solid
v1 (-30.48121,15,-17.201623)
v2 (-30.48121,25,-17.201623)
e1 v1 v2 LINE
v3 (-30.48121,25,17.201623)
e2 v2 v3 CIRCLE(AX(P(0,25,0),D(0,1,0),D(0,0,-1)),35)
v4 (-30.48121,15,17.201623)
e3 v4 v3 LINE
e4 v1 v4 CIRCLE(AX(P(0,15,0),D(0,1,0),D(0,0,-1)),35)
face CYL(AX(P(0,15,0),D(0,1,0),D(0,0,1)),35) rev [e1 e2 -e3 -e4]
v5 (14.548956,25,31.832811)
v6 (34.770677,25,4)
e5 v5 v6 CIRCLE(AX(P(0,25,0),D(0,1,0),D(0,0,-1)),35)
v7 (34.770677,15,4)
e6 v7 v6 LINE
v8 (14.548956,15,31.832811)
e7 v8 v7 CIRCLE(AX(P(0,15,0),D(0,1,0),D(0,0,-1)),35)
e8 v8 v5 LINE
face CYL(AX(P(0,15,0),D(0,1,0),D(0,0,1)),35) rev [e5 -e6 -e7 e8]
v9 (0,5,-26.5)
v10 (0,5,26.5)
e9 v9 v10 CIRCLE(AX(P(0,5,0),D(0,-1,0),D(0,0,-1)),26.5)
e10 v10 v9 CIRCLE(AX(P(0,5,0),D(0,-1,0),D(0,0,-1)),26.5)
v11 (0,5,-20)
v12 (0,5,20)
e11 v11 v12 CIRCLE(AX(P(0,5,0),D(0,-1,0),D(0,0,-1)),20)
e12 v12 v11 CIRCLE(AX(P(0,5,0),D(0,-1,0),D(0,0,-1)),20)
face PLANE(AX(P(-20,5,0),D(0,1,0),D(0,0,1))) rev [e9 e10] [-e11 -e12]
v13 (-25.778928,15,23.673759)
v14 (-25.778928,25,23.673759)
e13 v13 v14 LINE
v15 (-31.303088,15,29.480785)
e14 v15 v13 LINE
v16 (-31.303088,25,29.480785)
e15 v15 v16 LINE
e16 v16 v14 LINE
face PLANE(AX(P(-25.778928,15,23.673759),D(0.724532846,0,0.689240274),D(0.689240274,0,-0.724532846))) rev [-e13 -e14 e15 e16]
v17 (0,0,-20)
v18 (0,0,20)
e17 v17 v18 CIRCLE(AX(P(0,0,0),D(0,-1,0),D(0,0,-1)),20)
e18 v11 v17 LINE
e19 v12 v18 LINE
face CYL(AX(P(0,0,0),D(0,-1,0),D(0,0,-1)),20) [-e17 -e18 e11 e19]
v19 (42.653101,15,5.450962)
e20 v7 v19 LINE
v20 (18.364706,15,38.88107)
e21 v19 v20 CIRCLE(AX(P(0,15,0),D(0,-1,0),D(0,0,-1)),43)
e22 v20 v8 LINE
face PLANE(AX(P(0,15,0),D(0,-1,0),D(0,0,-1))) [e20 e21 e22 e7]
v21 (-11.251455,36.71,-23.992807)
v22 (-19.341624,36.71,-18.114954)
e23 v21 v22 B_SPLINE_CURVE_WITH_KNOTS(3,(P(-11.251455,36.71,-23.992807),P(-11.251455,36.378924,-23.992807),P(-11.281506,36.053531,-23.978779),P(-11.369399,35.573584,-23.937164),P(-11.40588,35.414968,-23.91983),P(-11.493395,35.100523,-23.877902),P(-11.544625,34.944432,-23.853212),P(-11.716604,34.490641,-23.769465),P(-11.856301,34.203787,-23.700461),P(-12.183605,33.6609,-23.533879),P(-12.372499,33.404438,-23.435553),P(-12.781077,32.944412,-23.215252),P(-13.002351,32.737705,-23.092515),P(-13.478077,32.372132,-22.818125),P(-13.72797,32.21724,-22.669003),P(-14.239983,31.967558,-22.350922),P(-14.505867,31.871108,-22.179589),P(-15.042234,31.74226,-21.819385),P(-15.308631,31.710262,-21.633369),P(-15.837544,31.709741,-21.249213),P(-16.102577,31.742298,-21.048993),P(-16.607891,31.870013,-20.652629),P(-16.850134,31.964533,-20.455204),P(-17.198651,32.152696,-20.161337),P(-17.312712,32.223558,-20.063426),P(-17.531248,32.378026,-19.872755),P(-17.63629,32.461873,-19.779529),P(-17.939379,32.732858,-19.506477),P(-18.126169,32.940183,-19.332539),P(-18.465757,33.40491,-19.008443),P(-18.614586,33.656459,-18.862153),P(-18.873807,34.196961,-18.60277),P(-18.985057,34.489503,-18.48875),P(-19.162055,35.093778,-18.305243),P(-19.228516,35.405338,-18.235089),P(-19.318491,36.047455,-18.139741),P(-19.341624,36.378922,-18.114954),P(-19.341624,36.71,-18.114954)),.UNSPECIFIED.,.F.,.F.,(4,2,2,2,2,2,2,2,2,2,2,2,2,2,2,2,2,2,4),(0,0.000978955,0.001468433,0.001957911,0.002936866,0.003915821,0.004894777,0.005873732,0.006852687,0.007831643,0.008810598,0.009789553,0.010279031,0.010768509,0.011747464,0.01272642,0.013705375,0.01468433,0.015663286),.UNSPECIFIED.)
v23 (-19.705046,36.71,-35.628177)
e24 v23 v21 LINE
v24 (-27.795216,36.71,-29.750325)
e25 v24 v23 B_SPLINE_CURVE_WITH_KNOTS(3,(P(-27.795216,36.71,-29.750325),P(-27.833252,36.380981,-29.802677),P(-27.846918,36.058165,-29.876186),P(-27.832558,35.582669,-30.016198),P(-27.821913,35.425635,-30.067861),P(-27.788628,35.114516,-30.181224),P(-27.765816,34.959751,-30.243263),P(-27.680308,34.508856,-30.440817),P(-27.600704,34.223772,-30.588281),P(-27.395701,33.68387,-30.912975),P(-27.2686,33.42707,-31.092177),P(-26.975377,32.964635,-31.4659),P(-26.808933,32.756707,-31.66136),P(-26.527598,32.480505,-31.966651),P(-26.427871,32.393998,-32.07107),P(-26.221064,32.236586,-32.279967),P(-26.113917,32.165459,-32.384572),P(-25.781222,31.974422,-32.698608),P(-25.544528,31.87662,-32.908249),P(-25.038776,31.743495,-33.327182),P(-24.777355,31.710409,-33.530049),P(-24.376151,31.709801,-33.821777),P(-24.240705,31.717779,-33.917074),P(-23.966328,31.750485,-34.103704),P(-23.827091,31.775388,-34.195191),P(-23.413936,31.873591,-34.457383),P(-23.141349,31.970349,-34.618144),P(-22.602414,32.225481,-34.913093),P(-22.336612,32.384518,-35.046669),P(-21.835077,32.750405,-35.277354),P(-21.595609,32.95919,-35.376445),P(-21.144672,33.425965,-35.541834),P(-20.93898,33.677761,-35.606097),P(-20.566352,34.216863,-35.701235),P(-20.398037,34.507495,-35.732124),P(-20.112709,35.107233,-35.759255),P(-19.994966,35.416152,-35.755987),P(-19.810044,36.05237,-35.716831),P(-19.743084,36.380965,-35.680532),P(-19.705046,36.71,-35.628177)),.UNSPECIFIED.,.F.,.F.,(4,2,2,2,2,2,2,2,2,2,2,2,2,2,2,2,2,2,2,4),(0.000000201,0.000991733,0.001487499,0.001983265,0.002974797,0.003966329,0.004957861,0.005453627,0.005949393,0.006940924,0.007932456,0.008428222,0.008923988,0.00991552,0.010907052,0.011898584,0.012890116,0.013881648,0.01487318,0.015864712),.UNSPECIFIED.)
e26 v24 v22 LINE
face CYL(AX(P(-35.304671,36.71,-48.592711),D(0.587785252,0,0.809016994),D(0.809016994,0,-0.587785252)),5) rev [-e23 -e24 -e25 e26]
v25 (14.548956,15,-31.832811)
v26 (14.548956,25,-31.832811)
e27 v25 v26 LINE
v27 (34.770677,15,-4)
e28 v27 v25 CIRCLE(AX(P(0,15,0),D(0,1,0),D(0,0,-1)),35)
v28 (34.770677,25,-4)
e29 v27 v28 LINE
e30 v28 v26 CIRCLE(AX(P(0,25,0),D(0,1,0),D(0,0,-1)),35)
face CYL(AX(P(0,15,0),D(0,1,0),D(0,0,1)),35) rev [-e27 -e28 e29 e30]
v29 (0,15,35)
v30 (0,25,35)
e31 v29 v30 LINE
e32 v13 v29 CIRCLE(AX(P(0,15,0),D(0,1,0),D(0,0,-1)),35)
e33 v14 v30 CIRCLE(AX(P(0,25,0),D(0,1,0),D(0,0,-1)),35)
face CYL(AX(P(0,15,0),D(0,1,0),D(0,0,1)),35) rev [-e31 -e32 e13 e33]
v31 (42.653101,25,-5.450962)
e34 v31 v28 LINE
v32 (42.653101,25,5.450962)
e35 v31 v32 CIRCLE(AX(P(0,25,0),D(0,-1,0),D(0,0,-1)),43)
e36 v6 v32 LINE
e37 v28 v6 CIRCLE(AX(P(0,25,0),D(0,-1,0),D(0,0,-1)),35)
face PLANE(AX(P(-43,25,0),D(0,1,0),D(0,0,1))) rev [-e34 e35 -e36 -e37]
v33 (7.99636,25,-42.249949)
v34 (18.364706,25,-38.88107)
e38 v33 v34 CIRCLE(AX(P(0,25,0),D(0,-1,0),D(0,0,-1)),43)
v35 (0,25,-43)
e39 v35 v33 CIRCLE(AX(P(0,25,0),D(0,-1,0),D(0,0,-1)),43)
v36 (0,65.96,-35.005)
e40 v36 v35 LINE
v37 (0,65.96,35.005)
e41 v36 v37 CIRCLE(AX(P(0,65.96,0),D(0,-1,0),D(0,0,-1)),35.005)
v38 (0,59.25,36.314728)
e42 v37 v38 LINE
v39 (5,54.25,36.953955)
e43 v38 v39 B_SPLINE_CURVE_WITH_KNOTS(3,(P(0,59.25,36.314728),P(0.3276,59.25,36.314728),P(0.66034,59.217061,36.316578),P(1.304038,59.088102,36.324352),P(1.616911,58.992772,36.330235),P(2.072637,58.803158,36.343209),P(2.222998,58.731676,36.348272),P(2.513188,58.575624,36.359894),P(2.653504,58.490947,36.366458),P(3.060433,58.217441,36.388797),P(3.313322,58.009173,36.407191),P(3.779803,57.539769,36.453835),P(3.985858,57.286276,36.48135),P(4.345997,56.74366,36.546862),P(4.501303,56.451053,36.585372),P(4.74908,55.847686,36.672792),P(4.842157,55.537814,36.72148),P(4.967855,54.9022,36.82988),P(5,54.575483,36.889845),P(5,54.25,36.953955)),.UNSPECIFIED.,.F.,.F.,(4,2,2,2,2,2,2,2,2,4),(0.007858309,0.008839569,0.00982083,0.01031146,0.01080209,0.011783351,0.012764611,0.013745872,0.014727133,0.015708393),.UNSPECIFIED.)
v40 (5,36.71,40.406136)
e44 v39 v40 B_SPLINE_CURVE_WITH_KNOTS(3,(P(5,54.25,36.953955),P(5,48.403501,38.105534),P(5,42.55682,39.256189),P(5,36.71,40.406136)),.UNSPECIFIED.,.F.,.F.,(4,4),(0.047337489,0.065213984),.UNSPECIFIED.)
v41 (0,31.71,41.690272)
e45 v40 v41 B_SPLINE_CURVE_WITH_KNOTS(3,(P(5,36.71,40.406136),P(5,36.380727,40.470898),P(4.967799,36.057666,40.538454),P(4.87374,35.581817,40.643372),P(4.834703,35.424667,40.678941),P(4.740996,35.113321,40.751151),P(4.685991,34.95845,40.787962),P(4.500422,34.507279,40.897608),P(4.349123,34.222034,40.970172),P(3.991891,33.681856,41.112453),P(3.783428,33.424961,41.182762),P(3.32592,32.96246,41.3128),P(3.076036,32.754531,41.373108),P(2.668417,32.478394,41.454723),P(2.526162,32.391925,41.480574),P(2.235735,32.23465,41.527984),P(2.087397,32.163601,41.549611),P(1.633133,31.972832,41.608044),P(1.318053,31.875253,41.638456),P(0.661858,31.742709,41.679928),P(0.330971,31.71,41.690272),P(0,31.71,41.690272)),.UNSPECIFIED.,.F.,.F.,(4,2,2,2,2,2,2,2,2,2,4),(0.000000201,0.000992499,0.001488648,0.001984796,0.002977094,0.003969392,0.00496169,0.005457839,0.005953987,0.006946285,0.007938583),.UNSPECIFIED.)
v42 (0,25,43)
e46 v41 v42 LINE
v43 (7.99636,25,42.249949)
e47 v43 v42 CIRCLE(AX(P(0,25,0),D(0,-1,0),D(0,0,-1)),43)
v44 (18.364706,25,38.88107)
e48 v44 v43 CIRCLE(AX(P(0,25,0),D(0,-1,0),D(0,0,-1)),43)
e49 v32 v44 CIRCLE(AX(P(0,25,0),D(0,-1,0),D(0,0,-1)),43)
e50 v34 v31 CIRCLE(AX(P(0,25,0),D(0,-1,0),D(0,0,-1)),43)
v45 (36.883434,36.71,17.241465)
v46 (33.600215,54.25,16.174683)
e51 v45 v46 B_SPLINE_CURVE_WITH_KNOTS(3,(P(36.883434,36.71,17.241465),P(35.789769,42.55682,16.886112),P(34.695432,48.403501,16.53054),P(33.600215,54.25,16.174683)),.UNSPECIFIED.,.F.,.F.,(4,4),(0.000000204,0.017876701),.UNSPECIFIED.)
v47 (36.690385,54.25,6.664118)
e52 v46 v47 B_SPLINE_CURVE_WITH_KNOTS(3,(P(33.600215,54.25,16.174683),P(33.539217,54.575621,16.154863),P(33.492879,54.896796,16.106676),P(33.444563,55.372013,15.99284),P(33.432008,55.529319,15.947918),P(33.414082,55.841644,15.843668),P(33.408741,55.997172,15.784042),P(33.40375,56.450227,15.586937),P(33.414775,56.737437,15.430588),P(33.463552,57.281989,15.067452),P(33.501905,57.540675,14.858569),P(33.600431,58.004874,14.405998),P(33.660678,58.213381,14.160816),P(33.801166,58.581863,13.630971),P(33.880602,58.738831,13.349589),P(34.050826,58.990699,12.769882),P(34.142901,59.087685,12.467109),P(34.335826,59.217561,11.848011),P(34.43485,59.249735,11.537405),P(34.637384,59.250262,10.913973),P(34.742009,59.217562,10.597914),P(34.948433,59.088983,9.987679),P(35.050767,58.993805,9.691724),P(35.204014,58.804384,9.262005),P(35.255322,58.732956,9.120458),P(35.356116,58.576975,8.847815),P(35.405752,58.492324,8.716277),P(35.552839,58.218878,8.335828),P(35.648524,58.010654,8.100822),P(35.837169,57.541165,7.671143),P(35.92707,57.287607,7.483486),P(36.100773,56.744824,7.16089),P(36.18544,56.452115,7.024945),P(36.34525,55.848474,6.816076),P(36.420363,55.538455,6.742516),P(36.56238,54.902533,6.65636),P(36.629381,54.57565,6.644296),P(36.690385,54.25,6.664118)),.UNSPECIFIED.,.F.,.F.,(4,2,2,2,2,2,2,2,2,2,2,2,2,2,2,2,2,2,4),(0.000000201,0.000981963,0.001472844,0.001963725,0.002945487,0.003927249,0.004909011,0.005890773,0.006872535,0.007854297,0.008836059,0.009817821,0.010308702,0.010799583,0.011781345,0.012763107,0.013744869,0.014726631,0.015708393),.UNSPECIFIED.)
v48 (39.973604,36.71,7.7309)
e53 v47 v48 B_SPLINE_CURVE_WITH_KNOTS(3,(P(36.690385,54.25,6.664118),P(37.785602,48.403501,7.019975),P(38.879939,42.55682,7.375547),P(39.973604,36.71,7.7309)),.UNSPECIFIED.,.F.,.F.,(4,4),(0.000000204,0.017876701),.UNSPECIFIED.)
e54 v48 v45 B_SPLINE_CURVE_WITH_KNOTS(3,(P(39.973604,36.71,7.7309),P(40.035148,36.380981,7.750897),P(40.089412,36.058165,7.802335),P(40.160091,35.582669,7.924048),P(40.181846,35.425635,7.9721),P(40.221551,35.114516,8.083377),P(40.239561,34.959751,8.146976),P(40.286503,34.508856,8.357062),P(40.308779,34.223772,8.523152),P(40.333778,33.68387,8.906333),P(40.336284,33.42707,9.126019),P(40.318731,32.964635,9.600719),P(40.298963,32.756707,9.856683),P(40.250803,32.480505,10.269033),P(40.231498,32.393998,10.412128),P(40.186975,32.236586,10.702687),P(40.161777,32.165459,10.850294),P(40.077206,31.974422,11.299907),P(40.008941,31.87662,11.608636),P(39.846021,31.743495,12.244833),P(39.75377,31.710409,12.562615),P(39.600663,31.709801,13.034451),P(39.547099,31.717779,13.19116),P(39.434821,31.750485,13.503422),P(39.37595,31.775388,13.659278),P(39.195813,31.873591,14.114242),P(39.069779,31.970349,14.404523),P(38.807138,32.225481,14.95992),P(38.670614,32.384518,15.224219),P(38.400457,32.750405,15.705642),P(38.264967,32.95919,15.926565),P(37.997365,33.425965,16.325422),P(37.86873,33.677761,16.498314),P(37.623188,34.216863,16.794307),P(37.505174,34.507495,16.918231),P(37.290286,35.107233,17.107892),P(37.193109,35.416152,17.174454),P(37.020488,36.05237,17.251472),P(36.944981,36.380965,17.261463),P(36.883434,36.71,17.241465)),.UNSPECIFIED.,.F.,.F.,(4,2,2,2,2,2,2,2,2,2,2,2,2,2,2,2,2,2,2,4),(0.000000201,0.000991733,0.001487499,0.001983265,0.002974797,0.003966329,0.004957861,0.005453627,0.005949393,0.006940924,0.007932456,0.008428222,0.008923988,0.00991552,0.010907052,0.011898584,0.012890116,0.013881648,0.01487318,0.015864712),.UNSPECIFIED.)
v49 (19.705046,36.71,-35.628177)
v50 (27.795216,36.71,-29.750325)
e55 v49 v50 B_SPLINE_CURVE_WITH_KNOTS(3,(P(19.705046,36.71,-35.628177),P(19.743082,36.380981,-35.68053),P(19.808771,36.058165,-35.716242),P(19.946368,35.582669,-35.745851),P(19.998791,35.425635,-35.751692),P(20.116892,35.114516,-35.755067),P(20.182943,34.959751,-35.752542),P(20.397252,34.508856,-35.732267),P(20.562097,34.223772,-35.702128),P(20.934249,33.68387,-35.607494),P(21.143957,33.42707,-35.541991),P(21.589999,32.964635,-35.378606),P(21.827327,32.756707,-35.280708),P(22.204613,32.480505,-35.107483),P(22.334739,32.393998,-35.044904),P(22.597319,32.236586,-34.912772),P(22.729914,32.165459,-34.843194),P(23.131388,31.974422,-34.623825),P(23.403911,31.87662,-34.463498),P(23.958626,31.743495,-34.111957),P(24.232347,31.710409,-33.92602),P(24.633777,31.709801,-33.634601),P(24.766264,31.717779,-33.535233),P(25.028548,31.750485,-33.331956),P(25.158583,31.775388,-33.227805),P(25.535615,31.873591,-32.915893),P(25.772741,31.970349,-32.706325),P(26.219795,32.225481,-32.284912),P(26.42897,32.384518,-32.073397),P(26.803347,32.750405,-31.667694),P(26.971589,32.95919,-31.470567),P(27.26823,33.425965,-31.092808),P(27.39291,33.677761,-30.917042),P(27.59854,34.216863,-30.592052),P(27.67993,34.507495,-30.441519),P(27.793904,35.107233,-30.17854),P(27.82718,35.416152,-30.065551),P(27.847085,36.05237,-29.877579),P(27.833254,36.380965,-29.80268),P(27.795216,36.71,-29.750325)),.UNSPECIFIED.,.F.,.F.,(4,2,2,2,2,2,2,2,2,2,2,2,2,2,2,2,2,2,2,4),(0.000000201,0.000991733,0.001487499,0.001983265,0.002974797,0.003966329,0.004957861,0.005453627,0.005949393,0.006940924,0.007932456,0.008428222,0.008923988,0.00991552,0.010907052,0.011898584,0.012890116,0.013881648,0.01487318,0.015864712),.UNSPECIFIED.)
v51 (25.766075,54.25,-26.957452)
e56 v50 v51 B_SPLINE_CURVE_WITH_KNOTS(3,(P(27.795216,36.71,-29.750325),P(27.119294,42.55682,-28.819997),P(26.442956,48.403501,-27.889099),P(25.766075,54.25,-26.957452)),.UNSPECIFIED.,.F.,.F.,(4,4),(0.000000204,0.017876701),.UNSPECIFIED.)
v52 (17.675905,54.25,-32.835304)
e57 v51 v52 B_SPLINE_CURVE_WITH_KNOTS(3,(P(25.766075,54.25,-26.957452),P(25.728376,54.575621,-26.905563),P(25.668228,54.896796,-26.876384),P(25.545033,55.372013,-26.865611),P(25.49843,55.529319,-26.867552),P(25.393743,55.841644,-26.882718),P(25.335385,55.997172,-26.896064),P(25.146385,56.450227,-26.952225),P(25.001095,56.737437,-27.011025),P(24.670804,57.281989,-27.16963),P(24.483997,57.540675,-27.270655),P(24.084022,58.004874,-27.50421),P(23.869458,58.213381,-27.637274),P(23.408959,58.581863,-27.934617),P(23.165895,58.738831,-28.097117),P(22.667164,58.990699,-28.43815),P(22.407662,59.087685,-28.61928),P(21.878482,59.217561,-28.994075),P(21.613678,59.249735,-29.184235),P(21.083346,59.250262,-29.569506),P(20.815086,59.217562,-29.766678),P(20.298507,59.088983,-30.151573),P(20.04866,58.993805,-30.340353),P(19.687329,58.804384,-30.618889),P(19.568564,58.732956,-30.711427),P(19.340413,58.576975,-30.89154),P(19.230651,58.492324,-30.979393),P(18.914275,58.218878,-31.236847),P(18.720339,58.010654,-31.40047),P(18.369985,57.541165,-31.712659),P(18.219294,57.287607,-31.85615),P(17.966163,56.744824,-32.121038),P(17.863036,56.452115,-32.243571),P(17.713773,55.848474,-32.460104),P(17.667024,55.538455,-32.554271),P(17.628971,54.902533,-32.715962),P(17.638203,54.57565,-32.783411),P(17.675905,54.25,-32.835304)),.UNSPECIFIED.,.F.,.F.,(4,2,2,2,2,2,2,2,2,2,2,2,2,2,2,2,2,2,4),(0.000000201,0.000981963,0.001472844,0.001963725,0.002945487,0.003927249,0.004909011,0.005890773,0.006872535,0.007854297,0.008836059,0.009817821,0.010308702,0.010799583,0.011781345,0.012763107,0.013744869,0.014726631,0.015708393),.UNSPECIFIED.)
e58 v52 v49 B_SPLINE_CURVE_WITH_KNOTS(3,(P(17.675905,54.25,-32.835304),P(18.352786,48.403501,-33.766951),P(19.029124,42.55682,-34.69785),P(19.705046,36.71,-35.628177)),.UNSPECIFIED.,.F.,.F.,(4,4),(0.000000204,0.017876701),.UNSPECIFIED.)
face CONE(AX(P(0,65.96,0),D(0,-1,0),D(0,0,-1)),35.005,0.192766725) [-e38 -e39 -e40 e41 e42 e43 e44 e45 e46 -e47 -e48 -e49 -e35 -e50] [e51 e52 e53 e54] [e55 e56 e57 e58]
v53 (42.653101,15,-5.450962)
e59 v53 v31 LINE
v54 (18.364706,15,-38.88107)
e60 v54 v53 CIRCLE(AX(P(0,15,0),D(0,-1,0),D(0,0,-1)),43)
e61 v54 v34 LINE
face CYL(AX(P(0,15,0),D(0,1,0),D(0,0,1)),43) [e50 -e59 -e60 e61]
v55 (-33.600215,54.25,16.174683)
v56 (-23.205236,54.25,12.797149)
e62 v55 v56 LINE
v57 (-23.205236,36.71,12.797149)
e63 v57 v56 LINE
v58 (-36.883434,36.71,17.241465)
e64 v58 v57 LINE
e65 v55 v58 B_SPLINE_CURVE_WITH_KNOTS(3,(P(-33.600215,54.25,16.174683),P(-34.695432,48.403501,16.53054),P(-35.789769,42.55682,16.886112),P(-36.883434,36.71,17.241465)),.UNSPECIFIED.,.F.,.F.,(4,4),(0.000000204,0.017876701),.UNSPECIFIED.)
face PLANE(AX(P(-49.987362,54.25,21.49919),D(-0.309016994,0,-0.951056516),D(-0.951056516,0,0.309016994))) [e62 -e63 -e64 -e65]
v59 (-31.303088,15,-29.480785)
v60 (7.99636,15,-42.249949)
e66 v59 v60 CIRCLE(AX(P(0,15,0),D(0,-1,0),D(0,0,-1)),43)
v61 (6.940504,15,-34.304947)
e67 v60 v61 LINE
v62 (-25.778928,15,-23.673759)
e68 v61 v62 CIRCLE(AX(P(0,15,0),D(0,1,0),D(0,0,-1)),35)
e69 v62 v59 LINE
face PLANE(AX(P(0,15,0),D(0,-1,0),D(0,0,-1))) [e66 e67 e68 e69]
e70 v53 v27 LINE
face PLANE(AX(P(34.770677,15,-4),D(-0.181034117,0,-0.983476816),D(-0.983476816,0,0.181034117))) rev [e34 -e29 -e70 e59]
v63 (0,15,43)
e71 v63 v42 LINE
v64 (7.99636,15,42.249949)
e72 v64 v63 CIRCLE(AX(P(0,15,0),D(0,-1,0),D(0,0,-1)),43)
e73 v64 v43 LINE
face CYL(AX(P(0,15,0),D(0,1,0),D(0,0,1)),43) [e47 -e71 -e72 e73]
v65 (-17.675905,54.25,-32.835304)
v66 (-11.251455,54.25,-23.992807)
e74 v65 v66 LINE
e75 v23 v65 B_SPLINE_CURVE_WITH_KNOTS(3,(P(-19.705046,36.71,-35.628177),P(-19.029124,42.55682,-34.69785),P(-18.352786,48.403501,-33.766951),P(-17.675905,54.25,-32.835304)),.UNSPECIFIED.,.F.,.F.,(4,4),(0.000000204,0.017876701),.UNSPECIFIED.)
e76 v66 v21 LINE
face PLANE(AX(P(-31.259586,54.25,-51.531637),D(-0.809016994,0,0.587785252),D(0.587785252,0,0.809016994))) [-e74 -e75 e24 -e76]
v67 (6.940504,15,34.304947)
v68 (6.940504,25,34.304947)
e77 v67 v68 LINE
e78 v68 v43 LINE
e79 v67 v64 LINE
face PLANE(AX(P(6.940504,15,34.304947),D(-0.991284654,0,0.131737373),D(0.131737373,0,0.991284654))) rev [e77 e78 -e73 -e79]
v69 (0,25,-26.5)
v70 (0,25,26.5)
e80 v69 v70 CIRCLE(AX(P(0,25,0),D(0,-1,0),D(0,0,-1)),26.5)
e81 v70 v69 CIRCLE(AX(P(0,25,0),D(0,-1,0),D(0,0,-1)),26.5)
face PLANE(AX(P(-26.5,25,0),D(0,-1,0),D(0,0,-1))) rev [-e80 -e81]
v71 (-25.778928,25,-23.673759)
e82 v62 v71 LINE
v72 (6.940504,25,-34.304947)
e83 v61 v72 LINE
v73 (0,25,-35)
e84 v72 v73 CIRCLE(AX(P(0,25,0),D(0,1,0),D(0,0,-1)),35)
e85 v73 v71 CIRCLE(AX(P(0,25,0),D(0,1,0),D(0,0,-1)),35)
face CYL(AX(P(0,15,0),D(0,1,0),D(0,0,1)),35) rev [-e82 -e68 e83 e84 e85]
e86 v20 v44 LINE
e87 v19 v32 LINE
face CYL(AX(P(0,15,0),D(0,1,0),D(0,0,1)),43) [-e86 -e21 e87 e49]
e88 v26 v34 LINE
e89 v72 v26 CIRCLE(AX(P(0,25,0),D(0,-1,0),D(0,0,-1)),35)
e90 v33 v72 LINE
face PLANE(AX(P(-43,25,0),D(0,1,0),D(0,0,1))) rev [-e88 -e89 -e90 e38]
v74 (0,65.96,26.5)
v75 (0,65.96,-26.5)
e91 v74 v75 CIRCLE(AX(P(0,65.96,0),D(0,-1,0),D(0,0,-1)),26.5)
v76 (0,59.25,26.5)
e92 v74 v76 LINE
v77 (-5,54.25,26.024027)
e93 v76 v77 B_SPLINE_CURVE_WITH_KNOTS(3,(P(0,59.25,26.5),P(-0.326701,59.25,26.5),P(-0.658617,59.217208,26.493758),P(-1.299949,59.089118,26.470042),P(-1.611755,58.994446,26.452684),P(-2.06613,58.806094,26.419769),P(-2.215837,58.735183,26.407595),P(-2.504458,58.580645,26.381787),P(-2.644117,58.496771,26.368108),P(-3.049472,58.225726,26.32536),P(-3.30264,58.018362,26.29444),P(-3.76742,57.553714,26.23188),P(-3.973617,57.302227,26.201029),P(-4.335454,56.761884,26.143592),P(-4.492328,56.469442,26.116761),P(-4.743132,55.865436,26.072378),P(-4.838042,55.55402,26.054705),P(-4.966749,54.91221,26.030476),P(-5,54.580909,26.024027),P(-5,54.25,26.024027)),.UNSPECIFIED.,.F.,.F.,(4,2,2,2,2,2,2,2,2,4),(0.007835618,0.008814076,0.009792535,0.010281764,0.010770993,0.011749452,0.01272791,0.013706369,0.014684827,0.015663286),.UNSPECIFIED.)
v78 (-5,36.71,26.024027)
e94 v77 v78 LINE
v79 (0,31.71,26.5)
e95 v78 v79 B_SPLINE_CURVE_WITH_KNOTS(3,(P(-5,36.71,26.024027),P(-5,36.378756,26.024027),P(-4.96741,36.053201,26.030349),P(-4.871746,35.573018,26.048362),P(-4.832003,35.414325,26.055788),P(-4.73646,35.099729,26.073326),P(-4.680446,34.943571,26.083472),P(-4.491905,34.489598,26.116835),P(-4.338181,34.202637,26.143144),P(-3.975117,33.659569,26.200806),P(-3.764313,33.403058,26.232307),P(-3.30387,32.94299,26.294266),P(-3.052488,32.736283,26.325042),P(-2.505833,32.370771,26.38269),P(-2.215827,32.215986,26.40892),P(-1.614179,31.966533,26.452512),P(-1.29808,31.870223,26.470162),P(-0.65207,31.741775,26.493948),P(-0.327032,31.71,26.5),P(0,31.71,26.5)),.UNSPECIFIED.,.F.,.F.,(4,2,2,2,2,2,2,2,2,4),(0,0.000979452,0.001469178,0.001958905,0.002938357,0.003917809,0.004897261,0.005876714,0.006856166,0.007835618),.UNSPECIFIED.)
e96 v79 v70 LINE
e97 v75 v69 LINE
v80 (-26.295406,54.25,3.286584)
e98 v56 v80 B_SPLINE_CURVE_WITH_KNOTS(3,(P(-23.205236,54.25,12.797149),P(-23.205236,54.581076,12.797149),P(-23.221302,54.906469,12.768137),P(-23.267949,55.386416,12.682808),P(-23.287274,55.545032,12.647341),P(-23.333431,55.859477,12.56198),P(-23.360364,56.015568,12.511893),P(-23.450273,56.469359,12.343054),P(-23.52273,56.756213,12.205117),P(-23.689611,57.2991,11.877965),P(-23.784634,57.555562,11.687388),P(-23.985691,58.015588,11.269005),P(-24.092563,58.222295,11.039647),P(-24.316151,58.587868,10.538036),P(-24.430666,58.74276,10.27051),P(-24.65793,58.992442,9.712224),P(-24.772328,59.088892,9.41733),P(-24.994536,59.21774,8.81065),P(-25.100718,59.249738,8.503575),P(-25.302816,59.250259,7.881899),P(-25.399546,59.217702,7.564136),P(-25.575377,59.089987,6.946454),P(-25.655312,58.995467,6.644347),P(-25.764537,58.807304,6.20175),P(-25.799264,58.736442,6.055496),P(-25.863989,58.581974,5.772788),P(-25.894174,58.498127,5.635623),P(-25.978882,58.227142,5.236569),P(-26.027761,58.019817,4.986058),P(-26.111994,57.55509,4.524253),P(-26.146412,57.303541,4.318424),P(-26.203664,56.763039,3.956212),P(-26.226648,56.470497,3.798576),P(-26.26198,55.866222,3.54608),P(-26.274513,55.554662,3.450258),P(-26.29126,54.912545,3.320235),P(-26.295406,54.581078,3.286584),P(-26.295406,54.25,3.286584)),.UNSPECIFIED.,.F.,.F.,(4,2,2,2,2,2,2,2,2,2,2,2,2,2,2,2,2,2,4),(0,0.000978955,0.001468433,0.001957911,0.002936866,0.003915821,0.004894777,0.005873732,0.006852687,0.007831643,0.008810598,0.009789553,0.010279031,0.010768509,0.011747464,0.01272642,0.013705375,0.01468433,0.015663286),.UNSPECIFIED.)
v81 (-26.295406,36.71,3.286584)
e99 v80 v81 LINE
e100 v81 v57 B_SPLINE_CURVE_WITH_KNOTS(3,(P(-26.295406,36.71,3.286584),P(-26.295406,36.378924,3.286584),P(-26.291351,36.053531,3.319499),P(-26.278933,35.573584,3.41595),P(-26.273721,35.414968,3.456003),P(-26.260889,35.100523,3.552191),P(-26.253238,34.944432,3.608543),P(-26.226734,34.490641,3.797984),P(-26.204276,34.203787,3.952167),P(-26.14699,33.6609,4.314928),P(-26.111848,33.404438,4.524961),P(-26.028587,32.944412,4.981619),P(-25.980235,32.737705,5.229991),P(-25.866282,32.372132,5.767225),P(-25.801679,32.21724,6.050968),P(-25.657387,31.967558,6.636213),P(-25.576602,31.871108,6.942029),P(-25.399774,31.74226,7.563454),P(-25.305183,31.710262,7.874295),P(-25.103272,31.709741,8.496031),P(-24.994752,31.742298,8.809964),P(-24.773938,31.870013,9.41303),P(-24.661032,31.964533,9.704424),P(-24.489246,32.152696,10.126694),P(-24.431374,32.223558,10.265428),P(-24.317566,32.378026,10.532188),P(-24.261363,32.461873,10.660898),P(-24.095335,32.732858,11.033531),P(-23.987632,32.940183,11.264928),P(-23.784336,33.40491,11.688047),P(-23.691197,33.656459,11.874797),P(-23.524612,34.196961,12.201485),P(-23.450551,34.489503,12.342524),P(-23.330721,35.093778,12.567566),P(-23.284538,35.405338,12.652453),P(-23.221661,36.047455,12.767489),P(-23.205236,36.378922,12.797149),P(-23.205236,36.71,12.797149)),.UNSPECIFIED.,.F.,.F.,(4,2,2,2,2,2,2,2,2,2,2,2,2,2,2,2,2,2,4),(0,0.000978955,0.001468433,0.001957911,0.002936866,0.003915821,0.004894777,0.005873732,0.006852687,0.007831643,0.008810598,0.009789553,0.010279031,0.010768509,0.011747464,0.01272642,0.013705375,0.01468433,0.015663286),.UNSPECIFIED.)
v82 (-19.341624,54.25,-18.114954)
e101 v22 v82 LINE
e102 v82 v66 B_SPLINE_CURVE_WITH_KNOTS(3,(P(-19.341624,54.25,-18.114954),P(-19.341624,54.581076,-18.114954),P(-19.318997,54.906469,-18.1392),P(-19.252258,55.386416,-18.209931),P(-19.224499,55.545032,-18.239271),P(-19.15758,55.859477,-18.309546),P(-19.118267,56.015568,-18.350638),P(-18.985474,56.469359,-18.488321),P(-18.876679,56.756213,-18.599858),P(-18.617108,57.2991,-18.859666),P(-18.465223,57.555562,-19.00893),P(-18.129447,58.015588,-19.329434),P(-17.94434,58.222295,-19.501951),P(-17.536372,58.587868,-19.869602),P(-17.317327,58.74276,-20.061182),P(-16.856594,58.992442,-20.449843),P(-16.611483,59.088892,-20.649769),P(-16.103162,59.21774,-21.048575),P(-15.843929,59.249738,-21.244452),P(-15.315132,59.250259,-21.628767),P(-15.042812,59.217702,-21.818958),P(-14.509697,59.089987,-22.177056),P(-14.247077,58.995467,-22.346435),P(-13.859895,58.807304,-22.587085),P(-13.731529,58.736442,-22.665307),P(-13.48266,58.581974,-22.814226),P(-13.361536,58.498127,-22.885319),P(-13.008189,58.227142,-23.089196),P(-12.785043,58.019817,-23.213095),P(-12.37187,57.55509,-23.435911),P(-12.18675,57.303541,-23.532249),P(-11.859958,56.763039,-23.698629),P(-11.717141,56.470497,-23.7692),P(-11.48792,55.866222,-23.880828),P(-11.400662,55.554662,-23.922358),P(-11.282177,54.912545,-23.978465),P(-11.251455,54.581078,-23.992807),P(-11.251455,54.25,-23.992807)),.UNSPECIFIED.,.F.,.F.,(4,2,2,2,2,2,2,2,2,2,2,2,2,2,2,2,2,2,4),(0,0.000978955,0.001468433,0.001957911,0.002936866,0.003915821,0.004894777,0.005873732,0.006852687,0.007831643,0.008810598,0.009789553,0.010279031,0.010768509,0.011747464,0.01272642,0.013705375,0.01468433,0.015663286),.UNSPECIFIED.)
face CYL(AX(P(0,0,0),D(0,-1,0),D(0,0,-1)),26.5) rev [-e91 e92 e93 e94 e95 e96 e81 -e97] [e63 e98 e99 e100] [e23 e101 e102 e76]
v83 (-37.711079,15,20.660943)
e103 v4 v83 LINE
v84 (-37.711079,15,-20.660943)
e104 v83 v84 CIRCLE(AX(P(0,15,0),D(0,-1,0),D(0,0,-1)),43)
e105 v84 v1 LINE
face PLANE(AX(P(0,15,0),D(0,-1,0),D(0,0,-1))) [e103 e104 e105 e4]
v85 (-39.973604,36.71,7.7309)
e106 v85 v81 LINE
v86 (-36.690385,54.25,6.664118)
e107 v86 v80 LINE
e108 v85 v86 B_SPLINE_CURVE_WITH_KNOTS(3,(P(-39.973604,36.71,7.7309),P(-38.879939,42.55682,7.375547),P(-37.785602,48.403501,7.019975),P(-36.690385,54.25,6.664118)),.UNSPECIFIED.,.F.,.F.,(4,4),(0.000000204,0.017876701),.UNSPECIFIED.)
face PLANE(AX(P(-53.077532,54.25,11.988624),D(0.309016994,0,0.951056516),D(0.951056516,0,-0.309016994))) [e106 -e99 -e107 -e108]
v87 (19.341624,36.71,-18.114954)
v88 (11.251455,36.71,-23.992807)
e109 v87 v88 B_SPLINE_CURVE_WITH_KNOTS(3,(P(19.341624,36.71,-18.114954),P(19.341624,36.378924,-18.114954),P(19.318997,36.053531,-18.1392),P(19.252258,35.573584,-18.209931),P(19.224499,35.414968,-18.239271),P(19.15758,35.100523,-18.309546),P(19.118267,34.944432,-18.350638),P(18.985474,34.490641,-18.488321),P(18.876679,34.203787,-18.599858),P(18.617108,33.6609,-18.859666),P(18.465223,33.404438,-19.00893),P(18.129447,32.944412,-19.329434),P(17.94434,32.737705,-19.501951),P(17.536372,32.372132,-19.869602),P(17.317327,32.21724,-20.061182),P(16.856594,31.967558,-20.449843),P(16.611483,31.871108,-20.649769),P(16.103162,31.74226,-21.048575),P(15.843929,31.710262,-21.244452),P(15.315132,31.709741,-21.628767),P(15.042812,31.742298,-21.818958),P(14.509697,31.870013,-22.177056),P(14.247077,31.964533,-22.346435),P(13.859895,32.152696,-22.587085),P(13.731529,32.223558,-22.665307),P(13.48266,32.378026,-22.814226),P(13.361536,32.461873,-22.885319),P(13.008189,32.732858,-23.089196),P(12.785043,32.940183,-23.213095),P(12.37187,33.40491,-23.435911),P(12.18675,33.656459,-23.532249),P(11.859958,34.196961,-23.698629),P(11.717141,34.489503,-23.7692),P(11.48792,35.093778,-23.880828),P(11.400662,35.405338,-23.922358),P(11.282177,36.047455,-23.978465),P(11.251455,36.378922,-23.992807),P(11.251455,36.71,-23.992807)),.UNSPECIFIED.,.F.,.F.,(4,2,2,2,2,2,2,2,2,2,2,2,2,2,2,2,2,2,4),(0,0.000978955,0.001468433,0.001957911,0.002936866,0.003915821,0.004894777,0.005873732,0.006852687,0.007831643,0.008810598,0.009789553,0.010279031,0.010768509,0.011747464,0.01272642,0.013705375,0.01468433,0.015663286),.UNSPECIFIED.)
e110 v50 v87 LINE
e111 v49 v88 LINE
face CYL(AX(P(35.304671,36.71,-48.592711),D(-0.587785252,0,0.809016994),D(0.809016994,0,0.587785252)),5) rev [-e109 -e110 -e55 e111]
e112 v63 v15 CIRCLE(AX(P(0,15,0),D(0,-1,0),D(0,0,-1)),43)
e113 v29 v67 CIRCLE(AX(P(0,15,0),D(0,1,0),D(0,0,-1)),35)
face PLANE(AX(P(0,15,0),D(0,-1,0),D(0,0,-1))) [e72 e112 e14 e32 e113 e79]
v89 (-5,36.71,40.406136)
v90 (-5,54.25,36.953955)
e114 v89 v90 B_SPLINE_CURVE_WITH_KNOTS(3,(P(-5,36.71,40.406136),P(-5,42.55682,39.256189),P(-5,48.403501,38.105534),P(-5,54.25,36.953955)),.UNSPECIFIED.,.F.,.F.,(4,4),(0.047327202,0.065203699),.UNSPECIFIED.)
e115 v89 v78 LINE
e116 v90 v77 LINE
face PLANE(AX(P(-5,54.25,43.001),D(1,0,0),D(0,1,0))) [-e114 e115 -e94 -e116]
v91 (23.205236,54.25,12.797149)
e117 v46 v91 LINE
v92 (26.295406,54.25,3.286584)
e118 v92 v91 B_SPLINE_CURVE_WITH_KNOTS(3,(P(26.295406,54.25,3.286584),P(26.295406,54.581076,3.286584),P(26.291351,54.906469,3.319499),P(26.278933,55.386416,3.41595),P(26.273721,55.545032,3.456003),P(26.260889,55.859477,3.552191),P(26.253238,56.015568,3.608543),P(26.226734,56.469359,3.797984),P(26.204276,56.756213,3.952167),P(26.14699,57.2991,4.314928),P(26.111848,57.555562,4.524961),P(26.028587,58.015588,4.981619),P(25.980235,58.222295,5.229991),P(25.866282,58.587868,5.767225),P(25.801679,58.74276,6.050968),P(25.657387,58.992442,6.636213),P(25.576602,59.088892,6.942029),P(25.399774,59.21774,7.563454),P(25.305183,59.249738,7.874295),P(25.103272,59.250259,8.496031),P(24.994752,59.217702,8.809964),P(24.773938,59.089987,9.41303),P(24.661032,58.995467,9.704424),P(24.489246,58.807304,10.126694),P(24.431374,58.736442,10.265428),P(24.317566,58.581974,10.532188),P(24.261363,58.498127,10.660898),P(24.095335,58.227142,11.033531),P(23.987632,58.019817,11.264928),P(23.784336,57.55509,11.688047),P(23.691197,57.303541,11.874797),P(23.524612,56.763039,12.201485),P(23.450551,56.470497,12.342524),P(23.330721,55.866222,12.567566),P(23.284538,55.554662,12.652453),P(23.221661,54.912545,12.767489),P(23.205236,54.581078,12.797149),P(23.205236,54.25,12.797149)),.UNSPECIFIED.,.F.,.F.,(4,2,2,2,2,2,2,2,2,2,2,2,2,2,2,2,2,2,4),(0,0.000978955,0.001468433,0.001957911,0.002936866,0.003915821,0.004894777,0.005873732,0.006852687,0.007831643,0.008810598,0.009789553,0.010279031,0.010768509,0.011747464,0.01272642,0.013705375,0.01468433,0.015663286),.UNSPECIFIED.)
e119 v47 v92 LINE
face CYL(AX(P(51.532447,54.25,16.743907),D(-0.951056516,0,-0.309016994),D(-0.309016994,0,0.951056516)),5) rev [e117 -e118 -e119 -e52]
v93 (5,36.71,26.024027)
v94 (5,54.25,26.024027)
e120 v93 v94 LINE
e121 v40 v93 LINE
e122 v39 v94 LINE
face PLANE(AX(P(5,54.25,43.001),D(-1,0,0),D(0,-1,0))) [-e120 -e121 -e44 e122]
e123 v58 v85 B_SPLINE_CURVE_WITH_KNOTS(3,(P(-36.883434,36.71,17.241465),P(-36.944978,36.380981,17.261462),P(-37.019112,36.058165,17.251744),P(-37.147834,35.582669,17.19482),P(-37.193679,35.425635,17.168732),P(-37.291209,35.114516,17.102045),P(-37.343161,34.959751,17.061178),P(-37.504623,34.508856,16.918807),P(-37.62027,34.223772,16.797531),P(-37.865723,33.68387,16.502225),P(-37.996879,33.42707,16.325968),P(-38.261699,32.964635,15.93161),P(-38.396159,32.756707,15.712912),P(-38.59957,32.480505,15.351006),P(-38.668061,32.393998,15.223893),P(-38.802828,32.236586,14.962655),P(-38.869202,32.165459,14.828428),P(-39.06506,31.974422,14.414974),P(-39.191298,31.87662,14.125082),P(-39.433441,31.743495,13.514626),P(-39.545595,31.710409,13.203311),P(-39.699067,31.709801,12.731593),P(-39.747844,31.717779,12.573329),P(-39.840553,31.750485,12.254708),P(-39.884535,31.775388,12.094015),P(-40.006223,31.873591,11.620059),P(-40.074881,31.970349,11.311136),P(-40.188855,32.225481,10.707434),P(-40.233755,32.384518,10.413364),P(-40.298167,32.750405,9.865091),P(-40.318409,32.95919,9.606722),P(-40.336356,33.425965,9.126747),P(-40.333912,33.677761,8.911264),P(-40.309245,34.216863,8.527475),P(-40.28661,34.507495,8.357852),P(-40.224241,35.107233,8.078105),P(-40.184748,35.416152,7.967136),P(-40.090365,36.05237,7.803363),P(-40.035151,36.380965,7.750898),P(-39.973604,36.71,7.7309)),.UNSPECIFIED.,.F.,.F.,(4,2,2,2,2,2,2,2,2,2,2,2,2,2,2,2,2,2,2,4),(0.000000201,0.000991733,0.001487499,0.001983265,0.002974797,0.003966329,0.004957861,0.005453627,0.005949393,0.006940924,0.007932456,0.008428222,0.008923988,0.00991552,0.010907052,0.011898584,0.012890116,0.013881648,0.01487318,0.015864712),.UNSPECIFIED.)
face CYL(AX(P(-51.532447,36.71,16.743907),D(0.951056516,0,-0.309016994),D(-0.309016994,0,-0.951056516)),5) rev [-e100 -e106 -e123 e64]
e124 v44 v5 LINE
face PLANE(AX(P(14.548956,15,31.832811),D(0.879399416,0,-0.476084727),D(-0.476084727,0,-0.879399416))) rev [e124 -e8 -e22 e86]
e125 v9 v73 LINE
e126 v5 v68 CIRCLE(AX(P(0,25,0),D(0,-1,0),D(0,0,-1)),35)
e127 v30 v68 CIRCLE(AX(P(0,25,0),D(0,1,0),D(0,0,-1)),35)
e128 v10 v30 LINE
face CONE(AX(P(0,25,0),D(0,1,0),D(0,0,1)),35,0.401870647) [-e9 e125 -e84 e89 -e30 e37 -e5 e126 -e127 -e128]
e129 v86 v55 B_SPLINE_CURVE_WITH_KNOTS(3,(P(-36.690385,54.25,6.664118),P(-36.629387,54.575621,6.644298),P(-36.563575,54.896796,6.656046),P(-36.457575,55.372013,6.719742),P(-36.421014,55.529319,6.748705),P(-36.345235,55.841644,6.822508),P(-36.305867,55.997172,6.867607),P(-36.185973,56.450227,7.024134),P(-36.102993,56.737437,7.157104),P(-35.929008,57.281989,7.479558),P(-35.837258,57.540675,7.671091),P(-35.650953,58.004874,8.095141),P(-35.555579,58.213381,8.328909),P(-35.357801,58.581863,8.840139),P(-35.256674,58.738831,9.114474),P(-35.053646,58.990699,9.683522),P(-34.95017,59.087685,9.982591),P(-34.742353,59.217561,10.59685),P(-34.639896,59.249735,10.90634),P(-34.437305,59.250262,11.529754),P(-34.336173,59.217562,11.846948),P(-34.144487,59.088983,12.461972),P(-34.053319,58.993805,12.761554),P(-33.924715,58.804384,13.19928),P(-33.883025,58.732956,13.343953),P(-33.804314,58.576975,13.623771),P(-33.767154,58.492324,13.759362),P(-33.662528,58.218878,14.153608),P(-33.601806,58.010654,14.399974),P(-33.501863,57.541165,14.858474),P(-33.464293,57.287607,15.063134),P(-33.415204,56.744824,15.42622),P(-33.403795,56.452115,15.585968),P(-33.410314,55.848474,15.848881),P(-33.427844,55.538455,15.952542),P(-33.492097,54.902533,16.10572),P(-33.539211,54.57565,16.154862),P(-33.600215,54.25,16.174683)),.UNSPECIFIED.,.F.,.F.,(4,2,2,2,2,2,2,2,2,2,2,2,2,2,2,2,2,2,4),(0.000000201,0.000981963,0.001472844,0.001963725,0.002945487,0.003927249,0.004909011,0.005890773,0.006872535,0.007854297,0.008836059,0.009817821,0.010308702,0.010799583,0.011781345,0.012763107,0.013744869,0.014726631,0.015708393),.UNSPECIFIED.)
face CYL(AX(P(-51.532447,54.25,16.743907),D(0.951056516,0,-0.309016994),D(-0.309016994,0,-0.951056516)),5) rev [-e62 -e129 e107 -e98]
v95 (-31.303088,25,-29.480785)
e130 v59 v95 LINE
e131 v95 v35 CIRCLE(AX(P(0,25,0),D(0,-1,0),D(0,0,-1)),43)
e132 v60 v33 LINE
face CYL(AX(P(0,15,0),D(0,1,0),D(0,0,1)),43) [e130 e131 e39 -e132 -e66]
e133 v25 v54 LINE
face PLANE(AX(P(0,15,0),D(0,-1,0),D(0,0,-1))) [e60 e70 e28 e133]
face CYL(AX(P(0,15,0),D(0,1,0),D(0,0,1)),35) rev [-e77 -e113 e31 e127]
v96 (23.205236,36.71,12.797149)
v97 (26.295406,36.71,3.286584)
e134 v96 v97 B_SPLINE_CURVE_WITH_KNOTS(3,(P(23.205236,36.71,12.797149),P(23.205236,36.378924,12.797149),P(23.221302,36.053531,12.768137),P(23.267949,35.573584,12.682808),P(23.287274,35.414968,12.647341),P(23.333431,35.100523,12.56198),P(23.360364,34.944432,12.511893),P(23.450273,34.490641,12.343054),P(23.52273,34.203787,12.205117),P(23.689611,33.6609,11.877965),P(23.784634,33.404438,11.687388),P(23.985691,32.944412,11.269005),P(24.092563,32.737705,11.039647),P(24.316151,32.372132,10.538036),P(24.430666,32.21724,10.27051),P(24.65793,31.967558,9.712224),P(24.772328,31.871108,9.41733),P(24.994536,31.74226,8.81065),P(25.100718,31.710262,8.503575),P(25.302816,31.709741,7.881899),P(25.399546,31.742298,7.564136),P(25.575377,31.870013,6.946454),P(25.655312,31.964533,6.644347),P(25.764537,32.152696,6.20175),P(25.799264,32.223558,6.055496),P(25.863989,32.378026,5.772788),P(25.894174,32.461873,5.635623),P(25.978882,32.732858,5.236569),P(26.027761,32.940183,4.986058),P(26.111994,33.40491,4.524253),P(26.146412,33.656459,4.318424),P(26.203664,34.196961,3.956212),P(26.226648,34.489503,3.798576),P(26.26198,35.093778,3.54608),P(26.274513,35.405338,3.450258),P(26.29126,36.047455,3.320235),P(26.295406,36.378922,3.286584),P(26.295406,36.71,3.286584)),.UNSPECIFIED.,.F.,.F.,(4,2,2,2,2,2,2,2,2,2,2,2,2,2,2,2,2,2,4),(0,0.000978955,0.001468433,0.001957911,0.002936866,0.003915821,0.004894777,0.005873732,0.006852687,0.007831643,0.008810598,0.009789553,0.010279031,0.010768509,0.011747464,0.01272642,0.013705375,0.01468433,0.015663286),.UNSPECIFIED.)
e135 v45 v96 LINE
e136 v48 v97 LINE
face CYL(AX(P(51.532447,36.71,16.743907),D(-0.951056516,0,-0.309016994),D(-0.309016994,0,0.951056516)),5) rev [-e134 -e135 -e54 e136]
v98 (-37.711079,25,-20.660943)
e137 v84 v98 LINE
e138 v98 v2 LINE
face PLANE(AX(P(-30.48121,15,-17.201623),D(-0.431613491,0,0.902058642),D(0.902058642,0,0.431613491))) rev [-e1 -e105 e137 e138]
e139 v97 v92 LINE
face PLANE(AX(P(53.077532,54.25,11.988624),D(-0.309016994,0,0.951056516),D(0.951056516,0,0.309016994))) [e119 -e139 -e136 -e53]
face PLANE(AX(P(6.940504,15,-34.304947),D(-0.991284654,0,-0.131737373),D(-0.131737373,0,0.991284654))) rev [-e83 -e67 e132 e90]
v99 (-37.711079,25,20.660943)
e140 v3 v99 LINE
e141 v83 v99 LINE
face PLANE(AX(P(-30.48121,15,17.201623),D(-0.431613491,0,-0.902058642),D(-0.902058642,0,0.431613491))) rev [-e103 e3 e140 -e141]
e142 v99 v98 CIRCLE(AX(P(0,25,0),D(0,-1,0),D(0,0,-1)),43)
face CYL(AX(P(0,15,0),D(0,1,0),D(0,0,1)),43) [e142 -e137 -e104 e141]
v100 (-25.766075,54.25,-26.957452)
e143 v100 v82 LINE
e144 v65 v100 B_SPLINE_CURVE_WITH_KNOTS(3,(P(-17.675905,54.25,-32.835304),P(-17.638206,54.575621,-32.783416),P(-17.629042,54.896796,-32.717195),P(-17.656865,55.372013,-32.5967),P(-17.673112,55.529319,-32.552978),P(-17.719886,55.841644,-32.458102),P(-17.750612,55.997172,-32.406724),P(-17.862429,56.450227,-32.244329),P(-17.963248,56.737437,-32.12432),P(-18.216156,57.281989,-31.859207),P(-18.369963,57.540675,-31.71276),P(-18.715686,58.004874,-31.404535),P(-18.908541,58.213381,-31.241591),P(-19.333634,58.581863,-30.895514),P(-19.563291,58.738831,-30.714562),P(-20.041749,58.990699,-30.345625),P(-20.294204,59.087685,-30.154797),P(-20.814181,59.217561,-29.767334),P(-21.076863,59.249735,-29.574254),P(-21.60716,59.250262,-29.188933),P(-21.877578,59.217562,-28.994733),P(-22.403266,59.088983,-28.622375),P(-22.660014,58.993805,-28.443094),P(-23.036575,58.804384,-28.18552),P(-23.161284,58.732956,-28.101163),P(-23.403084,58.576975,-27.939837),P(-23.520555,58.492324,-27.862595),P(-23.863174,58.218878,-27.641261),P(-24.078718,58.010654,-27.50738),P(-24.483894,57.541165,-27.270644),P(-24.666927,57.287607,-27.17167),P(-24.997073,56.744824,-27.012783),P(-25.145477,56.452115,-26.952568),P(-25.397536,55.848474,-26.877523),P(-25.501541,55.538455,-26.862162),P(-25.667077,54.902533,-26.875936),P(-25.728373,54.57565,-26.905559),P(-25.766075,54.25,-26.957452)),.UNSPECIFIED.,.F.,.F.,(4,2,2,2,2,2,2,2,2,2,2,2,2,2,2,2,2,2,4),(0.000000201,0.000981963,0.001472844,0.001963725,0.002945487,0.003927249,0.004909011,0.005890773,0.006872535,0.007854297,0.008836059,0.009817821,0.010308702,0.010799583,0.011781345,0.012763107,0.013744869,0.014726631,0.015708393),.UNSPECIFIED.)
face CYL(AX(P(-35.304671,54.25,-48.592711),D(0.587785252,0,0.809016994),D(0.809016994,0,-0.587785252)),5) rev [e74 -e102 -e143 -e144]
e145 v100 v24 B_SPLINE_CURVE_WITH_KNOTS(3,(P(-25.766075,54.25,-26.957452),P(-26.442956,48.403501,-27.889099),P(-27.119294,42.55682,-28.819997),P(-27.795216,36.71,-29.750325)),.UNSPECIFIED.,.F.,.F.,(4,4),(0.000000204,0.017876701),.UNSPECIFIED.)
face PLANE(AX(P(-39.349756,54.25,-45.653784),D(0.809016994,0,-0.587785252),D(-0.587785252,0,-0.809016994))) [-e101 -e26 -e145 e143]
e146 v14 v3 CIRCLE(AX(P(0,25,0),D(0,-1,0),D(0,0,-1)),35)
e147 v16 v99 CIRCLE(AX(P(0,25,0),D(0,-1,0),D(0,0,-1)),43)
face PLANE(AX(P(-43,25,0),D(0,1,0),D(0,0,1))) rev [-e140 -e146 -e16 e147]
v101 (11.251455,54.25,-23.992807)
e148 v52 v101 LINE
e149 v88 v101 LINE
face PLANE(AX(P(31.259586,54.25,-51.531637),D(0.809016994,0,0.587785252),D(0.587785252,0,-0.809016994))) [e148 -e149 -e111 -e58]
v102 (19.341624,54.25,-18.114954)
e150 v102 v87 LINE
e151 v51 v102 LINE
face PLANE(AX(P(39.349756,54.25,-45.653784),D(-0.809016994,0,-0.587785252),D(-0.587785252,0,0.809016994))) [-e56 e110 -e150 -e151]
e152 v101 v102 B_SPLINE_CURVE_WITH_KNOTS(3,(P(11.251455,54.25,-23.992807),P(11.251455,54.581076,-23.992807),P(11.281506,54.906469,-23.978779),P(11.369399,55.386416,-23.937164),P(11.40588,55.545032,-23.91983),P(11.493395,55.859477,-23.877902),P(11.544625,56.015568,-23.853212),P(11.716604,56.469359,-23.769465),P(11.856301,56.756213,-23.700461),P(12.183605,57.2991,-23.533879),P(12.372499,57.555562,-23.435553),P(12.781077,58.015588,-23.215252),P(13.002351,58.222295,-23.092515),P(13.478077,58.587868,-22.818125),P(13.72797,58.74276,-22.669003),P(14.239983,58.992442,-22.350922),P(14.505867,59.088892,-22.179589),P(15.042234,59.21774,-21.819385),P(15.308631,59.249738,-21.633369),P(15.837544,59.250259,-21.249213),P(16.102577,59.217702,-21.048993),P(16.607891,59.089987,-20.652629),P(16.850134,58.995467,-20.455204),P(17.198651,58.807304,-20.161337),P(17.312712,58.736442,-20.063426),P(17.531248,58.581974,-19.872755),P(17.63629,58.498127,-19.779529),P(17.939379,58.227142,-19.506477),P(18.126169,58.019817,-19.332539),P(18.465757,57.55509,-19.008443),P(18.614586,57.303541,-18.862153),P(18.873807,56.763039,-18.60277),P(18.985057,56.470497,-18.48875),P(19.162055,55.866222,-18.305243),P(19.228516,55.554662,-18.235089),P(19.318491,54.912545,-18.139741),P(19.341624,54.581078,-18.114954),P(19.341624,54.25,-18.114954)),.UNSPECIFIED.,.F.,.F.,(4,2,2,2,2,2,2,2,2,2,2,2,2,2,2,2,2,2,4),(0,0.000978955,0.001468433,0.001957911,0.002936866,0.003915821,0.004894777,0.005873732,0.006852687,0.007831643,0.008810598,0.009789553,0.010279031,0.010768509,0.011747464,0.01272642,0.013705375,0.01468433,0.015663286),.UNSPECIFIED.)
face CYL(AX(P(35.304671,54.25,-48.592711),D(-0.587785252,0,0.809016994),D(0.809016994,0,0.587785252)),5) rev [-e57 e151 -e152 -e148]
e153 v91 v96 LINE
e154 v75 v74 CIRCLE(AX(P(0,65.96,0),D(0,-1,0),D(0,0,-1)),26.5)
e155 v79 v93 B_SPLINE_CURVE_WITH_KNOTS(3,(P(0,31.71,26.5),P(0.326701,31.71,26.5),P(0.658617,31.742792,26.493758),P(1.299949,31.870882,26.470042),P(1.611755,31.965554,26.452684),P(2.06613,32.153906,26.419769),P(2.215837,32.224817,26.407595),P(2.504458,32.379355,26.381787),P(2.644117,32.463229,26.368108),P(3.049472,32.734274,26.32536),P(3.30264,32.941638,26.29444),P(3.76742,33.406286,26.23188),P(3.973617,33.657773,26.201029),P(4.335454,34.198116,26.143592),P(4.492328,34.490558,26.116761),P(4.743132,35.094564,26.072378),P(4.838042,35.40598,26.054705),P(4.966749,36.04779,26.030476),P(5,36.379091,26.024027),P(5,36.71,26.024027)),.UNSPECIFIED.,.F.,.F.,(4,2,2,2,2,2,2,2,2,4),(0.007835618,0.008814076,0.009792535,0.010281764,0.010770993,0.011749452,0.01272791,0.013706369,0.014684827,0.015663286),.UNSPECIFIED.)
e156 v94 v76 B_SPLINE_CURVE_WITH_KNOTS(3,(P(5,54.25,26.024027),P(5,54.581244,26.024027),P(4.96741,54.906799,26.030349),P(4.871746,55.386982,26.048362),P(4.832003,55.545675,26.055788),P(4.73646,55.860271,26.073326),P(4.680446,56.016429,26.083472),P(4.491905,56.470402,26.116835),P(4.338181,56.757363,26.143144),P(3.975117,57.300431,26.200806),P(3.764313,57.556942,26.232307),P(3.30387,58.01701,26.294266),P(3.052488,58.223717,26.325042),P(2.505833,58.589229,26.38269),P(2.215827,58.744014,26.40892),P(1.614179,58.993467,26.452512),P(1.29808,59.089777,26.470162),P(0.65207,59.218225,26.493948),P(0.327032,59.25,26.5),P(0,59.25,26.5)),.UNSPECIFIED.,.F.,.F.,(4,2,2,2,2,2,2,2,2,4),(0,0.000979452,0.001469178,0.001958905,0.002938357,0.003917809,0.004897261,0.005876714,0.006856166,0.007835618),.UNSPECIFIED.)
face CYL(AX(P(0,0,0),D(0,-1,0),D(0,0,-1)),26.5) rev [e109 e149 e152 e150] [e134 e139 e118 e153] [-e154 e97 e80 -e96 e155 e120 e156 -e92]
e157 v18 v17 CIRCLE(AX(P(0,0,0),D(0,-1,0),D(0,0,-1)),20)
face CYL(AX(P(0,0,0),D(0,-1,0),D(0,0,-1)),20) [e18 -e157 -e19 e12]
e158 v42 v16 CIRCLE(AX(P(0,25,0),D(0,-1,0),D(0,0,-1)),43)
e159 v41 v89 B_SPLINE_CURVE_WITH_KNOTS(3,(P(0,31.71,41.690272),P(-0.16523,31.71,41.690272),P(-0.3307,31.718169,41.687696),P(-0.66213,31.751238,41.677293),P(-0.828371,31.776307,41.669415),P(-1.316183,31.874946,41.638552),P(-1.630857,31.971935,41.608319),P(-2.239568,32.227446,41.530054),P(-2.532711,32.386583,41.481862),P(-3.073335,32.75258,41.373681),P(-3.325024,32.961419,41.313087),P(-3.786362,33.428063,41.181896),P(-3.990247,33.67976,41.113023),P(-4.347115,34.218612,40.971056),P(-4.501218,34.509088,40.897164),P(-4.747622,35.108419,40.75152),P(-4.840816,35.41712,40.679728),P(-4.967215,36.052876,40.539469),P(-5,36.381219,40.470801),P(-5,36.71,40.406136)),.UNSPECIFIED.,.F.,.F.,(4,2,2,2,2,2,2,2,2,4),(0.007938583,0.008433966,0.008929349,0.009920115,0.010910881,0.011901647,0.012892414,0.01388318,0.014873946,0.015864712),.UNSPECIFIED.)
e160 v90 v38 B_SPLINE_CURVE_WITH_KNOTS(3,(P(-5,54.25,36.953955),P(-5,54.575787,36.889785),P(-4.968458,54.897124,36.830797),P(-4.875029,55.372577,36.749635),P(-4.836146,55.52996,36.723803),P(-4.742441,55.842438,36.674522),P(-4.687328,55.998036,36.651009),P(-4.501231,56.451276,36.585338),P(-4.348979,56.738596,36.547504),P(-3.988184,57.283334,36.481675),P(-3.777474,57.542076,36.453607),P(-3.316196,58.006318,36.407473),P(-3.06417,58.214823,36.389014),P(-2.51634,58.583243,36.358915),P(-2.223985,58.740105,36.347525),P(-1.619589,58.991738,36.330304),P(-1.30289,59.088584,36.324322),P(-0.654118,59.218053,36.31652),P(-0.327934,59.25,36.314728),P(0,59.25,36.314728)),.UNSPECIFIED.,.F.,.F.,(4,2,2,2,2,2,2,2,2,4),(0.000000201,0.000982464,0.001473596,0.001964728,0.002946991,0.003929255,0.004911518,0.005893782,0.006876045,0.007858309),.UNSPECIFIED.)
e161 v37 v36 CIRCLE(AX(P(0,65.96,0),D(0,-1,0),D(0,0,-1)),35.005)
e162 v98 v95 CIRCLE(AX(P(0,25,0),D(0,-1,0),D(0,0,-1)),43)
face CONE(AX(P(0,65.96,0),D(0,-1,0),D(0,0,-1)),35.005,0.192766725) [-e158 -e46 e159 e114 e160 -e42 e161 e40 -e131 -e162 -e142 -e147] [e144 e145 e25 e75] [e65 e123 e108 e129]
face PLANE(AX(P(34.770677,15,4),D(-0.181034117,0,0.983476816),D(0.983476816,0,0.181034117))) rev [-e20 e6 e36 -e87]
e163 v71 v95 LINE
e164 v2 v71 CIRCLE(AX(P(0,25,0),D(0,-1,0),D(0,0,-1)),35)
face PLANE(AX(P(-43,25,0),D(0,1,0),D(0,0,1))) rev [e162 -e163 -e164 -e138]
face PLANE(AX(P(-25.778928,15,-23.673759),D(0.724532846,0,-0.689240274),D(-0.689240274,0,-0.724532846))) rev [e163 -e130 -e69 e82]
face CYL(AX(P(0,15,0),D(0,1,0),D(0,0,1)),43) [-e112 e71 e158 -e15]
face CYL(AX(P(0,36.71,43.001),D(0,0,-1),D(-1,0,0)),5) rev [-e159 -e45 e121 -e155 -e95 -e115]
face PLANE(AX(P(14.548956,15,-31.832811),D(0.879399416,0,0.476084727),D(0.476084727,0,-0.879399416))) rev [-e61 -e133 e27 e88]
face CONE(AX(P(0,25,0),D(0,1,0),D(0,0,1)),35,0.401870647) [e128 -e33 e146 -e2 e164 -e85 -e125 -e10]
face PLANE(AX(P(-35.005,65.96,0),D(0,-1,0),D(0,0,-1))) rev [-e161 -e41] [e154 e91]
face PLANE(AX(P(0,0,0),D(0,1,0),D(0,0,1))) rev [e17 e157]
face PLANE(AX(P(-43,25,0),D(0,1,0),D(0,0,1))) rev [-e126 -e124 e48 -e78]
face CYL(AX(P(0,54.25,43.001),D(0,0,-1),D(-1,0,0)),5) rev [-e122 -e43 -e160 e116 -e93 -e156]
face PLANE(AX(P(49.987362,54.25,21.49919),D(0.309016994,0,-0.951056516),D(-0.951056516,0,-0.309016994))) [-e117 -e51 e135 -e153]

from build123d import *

# Parameters (mm, degrees)
WALL_SLOT_CUT_REACH        = 91.715
WALL_SLOT_PATTERN_5X_COUNT = 5
BASE_TABS_DEPTH            = 10


with BuildPart() as part:
    # Housing Profile Sketch → Tapered Housing Body (revolve)
    with BuildSketch(Plane.XY, mode=Mode.PRIVATE) as tapered_housing_body_sk:
        Polygon((0, 0), (-20, 0), (-20, 5), (-26.5, 5), (-35, 25), (-43, 25), (-35.005, 65.96), (-26.5, 65.96), (-26.5, 25), (0, 25), align=None)
    revolve(tapered_housing_body_sk.sketch.rotate(Axis((0, 0, 0), (0, 1, 0)), 270), axis=Axis((0, 0, 0), (0, 1, 0)))

    # Wall Slot Cut: up to this cone (the profile starts inside it)
    wall_slot_cut_end = Plane(origin=(0, 45.48, 0), z_dir=(0, -1, 0)) * Cone(13.390099792, 64.614900208, 262.435, mode=Mode.PRIVATE)
    # Wall Slot Sketch → Wall Slot Cut (cut, up to the surface)
    with BuildSketch(Plane.XY, mode=Mode.PRIVATE) as wall_slot_cut_sk1:
        with BuildLine():
            Line((5, 54.25), (5, 36.71))
            ThreePointArc((5, 36.71), (0, 31.71), (-5, 36.71))
            Line((-5, 36.71), (-5, 54.25))
            ThreePointArc((-5, 54.25), (0, 59.25), (5, 54.25))
        make_face()
    wall_slot_cut_tool1 = extrude(wall_slot_cut_sk1.sketch, amount=WALL_SLOT_CUT_REACH, mode=Mode.PRIVATE) & wall_slot_cut_end
    wall_slot_cut = wall_slot_cut_tool1.solids().sort_by_distance((0, 45.48, 0))[0]
    add(wall_slot_cut, mode=Mode.SUBTRACT)

    # Wall Slot Pattern 5x: Wall Slot Cut ×5 about axis
    wall_slot_pattern_5x_axis = Axis((0, 0, 0), (0, 1, 0))
    for i in range(1, WALL_SLOT_PATTERN_5X_COUNT):
        add(wall_slot_cut.rotate(wall_slot_pattern_5x_axis, i * 360 / WALL_SLOT_PATTERN_5X_COUNT), mode=Mode.SUBTRACT)

    # Base Tab Sketch → Base Tabs (add)
    with BuildSketch(Plane.XZ.offset(-25)):
        with BuildLine():
            Line((34.770677301, 4), (42.65310085, 5.450962103))
            ThreePointArc((42.65310085, 5.450962103), (34.787730758, 25.274765849), (18.364706053, 38.881069579))
            Line((18.364706053, 38.881069579), (14.548956257, 31.832811246))
            ThreePointArc((14.548956257, 31.832811246), (28.315594803, 20.57248383), (34.770677301, 4))
        make_face()
        with BuildLine():
            Line((34.770677301, -4), (42.65310085, -5.450962103))
            ThreePointArc((42.65310085, -5.450962103), (34.787730758, -25.274765849), (18.364706053, -38.881069579))
            Line((18.364706053, -38.881069579), (14.548956257, -31.832811246))
            ThreePointArc((14.548956257, -31.832811246), (28.315594803, -20.57248383), (34.770677301, -4))
        make_face()
        with BuildLine():
            Line((6.940504127, -34.304947201), (7.996359998, -42.249949429))
            ThreePointArc((7.996359998, -42.249949429), (-13.287730758, -40.895430201), (-31.303088316, -29.480784621))
            Line((-31.303088316, -29.480784621), (-25.778927834, -23.673759307))
            ThreePointArc((-25.778927834, -23.673759307), (-10.815594803, -33.28697807), (6.940504127, -34.304947201))
        make_face()
        with BuildLine():
            Line((-30.481209852, -17.201623352), (-37.711078585, -20.660942668))
            ThreePointArc((-37.711078585, -20.660942668), (-43, 0), (-37.711078585, 20.660942668))
            Line((-37.711078585, 20.660942668), (-30.481209852, 17.201623353))
            ThreePointArc((-30.481209852, 17.201623353), (-35, 0), (-30.481209852, -17.201623352))
        make_face()
        with BuildLine():
            Line((-25.778927834, 23.673759307), (-31.303088316, 29.480784621))
            ThreePointArc((-31.303088316, 29.480784621), (-13.287730758, 40.895430201), (7.996359998, 42.249949429))
            Line((7.996359998, 42.249949429), (6.940504127, 34.304947201))
            ThreePointArc((6.940504127, 34.304947201), (-10.815594803, 33.28697807), (-25.778927834, 23.673759307))
        make_face()
    extrude(amount=BASE_TABS_DEPTH)


solid = part.part
